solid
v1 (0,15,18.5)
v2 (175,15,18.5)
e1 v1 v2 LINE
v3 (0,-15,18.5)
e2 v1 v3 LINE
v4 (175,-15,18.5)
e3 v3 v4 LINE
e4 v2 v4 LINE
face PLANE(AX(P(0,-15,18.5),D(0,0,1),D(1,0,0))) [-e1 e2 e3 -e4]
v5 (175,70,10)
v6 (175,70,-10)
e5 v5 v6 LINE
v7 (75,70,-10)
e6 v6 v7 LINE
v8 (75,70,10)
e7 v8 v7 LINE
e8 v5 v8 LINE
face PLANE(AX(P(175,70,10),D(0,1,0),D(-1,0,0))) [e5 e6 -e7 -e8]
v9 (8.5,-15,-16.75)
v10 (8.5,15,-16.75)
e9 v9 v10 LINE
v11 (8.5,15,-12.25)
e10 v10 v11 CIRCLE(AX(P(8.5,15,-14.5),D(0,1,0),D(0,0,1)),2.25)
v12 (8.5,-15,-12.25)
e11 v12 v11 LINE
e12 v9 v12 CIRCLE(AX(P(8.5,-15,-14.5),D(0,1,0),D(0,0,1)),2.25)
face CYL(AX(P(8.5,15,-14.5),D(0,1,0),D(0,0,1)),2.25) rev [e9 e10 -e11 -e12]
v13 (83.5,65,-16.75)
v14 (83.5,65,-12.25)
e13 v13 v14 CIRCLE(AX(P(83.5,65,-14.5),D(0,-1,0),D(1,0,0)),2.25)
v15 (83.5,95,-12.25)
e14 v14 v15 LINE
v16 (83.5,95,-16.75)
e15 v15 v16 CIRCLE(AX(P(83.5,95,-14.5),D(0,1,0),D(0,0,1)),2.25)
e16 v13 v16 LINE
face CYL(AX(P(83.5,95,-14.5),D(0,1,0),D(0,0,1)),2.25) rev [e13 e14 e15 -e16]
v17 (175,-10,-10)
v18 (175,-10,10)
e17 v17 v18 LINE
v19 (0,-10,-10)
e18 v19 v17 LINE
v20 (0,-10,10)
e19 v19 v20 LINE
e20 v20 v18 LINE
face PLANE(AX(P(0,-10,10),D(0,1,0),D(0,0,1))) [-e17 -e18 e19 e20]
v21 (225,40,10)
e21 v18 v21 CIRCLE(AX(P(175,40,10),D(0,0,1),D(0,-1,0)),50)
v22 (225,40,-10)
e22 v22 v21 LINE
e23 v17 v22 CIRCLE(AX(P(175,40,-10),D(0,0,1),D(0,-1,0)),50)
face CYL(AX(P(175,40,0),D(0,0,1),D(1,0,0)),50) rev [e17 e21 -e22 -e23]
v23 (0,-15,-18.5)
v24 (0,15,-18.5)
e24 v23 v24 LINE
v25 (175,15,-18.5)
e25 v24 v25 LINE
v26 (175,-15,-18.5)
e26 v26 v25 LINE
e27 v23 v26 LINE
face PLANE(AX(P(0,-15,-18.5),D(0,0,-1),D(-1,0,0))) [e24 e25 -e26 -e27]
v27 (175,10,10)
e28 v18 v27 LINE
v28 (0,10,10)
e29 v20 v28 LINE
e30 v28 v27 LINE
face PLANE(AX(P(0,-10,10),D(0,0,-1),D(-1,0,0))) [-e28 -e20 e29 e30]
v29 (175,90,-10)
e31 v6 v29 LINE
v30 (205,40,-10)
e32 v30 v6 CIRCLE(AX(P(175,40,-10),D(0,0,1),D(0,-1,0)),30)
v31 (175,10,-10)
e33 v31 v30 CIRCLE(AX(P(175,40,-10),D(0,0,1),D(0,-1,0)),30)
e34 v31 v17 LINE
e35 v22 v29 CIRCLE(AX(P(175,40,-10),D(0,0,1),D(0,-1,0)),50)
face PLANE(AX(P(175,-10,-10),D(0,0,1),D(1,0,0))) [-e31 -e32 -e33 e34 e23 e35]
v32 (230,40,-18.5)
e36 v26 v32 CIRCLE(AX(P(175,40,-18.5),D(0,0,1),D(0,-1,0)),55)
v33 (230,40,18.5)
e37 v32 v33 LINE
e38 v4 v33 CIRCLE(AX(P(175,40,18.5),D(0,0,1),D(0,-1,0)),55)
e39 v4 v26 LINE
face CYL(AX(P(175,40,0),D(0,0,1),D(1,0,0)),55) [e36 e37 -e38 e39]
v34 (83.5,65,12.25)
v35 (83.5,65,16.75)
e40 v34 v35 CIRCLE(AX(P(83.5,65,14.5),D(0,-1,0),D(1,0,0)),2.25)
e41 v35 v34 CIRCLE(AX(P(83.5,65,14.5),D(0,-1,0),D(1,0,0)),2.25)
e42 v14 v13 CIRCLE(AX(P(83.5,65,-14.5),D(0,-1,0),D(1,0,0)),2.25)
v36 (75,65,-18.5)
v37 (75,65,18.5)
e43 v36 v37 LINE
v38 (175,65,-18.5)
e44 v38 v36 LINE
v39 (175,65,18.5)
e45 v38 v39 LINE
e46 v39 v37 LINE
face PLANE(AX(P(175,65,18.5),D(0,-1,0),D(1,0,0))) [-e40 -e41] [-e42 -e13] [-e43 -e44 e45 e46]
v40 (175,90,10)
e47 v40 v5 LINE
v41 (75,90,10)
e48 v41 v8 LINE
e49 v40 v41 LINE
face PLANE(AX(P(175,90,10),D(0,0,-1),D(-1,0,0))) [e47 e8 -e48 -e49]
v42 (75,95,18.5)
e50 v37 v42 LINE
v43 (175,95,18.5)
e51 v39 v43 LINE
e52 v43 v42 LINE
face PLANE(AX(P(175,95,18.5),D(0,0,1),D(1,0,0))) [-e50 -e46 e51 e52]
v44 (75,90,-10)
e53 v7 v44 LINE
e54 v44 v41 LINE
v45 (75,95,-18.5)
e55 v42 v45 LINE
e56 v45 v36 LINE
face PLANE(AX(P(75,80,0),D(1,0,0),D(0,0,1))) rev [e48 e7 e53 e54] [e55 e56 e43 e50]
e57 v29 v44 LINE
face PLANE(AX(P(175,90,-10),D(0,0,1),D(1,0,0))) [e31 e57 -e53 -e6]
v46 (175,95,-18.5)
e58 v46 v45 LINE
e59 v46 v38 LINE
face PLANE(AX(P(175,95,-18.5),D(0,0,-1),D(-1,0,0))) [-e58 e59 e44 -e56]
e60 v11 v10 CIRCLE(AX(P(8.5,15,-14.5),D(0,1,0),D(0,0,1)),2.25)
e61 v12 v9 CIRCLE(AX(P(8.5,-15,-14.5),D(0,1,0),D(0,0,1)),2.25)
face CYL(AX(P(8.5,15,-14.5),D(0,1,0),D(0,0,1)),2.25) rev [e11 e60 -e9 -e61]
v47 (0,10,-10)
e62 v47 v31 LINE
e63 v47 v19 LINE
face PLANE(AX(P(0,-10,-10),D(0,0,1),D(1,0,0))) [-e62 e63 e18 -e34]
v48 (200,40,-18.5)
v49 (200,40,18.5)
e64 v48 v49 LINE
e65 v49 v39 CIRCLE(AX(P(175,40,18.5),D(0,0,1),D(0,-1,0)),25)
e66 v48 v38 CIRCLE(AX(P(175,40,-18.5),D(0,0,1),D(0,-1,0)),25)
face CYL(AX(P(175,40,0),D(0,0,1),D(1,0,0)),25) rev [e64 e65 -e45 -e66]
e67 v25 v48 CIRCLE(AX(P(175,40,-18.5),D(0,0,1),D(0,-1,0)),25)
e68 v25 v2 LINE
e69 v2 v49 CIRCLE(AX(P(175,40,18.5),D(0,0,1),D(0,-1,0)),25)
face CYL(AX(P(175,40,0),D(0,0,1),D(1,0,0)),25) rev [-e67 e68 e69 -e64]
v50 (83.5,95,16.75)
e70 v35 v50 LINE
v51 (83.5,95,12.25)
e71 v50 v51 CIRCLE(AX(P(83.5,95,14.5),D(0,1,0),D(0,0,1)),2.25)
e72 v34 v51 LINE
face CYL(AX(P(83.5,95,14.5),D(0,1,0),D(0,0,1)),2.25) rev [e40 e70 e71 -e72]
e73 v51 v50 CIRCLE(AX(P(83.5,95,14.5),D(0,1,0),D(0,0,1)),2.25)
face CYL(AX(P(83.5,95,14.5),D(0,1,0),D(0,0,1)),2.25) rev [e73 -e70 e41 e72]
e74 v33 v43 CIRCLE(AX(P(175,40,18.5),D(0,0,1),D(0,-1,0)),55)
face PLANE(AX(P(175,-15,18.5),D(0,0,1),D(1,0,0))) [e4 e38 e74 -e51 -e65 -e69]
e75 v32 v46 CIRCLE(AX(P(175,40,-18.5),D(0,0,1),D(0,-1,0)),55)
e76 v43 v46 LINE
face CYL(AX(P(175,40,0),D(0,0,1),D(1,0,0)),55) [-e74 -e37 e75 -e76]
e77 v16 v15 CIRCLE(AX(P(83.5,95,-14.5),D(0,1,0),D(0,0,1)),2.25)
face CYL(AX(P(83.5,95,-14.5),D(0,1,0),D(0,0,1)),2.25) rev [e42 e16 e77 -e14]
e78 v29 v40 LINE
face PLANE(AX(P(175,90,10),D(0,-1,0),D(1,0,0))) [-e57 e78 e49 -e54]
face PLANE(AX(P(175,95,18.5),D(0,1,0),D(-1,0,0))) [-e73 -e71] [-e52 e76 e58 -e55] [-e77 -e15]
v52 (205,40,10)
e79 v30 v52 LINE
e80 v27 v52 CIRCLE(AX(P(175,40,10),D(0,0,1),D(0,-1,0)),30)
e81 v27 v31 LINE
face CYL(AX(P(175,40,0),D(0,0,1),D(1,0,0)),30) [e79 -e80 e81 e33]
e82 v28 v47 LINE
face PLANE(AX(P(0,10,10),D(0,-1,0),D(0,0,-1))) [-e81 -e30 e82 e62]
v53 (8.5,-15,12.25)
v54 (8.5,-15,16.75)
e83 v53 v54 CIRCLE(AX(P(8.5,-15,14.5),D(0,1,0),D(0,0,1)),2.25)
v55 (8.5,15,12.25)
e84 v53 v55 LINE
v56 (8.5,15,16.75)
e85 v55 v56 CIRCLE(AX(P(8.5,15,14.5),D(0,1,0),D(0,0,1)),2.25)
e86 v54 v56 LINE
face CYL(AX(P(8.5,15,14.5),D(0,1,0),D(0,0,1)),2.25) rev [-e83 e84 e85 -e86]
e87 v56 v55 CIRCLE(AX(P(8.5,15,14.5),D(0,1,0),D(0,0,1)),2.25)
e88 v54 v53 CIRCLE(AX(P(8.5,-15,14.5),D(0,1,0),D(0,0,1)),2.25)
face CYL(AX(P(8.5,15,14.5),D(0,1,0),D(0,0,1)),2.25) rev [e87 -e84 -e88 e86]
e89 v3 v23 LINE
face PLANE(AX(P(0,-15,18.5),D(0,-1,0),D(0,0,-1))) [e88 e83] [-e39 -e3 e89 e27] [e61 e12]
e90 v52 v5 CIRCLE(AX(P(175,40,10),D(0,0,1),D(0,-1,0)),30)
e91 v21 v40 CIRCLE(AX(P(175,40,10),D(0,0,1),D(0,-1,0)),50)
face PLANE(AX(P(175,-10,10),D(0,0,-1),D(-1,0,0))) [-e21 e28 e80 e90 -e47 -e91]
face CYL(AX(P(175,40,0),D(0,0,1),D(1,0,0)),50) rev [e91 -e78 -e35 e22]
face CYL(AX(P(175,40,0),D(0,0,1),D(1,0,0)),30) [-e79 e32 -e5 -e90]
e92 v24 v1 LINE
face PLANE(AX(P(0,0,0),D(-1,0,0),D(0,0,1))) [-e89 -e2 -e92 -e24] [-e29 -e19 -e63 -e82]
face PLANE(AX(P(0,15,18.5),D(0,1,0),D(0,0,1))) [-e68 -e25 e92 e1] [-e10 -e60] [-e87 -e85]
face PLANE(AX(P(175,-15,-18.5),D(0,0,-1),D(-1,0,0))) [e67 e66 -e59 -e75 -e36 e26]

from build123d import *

# Parameters (mm, degrees)
SKETCH1_W                = 37
SKETCH1_H                = 30
SKETCH1_W_2              = 20
SKETCH1_H_2              = 20
M4_CLEARANCE_HOLE1_D     = 4.5
M4_CLEARANCE_HOLE2_D     = 4.5
M4_CLEARANCE_HOLE2_DEPTH = 50
M4_CLEARANCE_HOLE2_TIP   = 1.351936393


with BuildPart() as part:
    # Sweep1: sweep along a path in Sketch2
    with BuildLine(Plane.XY) as sweep1_path:
        Line((0, 0), (175, 0))
        ThreePointArc((175, 0), (215, 40), (175, 80))
        Line((175, 80), (75, 80))
    # Sketch1 → Sweep1 (sweep)
    with BuildSketch(Plane(origin=(0, 0, 0), x_dir=(0, 0, -1), z_dir=(1, 0, 0))):
        Rectangle(SKETCH1_W, SKETCH1_H)
        Rectangle(SKETCH1_W_2, SKETCH1_H_2, mode=Mode.SUBTRACT)
    sweep(path=sweep1_path.line)

    # M4 Clearance Hole1 (through all)
    with Locations(Plane(origin=(0, 15, 0), x_dir=(1, 0, 0), z_dir=(0, 1, 0))):
        with Locations((8.5, 14.5), (8.5, -14.5)):
            Hole(M4_CLEARANCE_HOLE1_D / 2)

    # M4 Clearance Hole2
    with Locations(Plane(origin=(0, 95, 0), x_dir=(1, 0, 0), z_dir=(0, 1, 0))):
        with Locations((83.5, -14.5), (83.5, 14.5)):
            Hole(M4_CLEARANCE_HOLE2_D / 2, depth=M4_CLEARANCE_HOLE2_DEPTH)
            with Locations((0, 0, -(M4_CLEARANCE_HOLE2_DEPTH + M4_CLEARANCE_HOLE2_TIP / 2))):  # 118° drill point
                Cone(0, M4_CLEARANCE_HOLE2_D / 2, M4_CLEARANCE_HOLE2_TIP, mode=Mode.SUBTRACT)


solid = part.part
